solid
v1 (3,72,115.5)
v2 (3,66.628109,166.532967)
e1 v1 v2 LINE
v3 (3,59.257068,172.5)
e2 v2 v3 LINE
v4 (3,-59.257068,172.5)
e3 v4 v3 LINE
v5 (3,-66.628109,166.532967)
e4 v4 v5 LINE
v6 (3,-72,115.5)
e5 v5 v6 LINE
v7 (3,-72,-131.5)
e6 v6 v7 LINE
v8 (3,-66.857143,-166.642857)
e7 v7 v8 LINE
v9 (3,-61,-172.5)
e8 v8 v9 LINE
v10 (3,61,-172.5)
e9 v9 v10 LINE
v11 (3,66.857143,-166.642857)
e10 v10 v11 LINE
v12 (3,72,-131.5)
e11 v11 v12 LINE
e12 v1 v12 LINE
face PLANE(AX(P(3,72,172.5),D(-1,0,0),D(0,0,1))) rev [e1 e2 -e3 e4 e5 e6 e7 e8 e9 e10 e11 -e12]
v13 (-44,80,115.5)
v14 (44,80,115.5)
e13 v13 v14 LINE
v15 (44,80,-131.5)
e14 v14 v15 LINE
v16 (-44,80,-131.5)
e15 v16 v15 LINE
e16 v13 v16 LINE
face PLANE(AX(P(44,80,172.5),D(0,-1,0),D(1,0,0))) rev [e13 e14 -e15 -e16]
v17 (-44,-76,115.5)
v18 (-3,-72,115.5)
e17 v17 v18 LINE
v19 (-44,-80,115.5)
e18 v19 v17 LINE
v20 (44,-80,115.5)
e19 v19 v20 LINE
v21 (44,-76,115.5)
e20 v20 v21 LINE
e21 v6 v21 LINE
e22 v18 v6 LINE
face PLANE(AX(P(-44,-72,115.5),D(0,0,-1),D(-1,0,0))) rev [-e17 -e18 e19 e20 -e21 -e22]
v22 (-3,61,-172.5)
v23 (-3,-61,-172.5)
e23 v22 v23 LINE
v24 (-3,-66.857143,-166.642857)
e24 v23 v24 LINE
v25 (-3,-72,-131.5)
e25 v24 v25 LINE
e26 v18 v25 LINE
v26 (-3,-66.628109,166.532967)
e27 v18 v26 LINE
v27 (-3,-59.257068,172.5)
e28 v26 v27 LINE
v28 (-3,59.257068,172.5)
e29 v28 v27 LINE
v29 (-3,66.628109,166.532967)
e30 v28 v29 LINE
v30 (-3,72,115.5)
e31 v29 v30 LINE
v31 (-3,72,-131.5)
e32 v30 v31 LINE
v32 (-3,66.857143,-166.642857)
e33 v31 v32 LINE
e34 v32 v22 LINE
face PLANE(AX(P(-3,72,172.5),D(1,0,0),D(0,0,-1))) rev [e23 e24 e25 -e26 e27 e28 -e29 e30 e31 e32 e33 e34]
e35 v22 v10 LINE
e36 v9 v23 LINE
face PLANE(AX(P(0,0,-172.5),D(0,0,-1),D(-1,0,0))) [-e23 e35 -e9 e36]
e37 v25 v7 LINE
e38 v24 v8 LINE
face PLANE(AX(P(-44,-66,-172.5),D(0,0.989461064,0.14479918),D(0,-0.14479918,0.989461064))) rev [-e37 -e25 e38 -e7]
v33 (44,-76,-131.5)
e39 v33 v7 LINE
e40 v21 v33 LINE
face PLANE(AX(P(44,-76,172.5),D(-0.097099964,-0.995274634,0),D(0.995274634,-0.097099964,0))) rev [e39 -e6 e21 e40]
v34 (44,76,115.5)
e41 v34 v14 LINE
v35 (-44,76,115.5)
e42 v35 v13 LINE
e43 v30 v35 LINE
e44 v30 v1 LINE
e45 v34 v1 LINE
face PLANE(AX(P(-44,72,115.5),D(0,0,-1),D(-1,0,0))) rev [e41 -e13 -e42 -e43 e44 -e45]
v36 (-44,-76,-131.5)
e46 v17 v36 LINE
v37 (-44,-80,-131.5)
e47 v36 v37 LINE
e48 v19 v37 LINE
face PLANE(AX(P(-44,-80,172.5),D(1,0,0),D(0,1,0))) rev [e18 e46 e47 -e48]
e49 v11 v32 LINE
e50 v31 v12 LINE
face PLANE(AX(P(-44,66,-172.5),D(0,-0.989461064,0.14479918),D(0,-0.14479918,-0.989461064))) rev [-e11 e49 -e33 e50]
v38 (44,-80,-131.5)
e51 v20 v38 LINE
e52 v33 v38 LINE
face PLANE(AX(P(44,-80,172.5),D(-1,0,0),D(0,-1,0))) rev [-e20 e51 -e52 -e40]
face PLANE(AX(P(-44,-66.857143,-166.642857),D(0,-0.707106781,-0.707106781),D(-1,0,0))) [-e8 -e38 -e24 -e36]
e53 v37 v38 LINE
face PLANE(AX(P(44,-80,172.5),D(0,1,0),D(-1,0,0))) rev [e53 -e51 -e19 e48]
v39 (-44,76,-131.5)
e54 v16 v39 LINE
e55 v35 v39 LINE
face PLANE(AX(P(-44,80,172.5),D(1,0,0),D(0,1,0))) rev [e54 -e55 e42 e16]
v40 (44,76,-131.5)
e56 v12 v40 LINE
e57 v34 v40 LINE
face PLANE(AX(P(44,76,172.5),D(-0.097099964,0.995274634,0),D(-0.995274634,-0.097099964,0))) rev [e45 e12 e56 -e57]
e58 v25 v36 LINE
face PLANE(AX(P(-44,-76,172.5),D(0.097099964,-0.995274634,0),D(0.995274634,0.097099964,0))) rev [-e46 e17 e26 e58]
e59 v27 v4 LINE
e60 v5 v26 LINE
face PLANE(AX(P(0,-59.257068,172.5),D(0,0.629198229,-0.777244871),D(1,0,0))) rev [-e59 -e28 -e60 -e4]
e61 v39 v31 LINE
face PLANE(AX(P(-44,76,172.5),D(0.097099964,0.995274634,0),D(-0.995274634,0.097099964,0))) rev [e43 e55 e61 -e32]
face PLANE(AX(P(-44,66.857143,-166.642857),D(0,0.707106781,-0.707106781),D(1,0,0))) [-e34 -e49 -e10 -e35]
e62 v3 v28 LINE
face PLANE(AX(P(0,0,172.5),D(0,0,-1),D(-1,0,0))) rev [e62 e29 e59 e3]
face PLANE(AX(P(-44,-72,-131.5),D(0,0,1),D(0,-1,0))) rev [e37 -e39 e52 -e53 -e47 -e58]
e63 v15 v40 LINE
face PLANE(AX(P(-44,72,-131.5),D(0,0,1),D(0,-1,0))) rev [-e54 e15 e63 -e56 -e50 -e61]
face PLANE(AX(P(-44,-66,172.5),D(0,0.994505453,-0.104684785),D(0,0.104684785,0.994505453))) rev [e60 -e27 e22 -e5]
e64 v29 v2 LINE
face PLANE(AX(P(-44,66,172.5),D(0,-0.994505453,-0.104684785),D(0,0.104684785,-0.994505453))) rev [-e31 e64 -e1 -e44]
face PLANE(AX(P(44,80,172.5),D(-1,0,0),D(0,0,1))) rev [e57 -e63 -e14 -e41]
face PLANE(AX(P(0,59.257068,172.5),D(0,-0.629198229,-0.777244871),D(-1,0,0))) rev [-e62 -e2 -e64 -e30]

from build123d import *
from OCP.BRepFilletAPI import BRepFilletAPI_MakeChamfer

# Parameters (mm, degrees)
EXTRUDE_1_DEPTH          = 172.5
CUT_EXTRUDE_1_DEPTH      = 196.172359723
CUT_EXTRUDE_1_DEPTH_BACK = 196.172359723
CHAMFER_1_SIZE           = 6
CHAMFER_1_SIZE2          = 6.742931709
CHAMFER_2_SIZE           = 5
CHAMFER_2_SIZE2          = 5.919528387
CHAMFER_2_EDGE_2_SIZE    = 5
CHAMFER_2_EDGE_2_SIZE2   = 5.919528387


with BuildPart() as part:
    # 草图1 → 凸台-拉伸1 (new, symmetric)
    with BuildSketch(Plane.XY):
        Polygon((44, 80), (-44, 80), (-44, 76), (-3, 72), (-3, -72), (-44, -76), (-44, -80), (44, -80), (44, -76), (3, -72), (3, 72), (44, 76), align=None)
    extrude(amount=EXTRUDE_1_DEPTH, both=True)

    # 草图3 → 切除-拉伸1 (cut, two sides: drawn at the far end of the back side and taken through both)
    with BuildSketch(Plane(origin=(0, 0, 0), x_dir=(0, 0, -1), z_dir=(1, 0, 0)).offset(-CUT_EXTRUDE_1_DEPTH_BACK)):
        Polygon((-172.5, 66), (-115.5, 72), (-115.5, 80), (-172.5, 80), align=None)
        Polygon((172.5, 80), (172.5, 66), (131.5, 72), (131.5, 80), align=None)
        Polygon((172.5, -66), (131.5, -72), (131.5, -80), (172.5, -80), align=None)
        Polygon((-172.5, -80), (-172.5, -66), (-115.5, -72), (-115.5, -80), align=None)
    extrude(amount=CUT_EXTRUDE_1_DEPTH + CUT_EXTRUDE_1_DEPTH_BACK, mode=Mode.SUBTRACT)

    # 倒角1: one chamfer whose edges measure the first distance from different faces: ONE call of the kernel's chamfer builder (chamfer() names one face for all edges)
    chamfer_1_edges_1 = [part.edges().sort_by_distance(p)[0] for p in [
        (0, 66, 172.5),
    ]]
    chamfer_1_side_1 = [part.faces().sort_by_distance(p)[0] for p in [
        (0, 69, 144),
    ]]
    chamfer_1_edges_2 = [part.edges().sort_by_distance(p)[0] for p in [
        (0, -66, 172.5),
    ]]
    chamfer_1_side_2 = [part.faces().sort_by_distance(p)[0] for p in [
        (0, -69, 144),
    ]]
    chamfer_1 = BRepFilletAPI_MakeChamfer(part.part.solid().wrapped)
    for e in chamfer_1_edges_1:
        chamfer_1.Add(CHAMFER_1_SIZE, CHAMFER_1_SIZE2, e.wrapped, chamfer_1_side_1[0].wrapped)  # the first distance lies on this face
    for e in chamfer_1_edges_2:
        chamfer_1.Add(CHAMFER_1_SIZE, CHAMFER_1_SIZE2, e.wrapped, chamfer_1_side_2[0].wrapped)  # the first distance lies on this face
    add(Compound.cast(chamfer_1.Shape()), mode=Mode.REPLACE)

    # 倒角2
    chamfer_2_edges = [part.edges().sort_by_distance(p)[0] for p in [
        (0, 66, -172.5),
    ]]
    chamfer_2_side = [part.faces().sort_by_distance(p)[0] for p in [
        (0, 0, -172.5),
    ]]
    chamfer(chamfer_2_edges, length=CHAMFER_2_SIZE, length2=CHAMFER_2_SIZE2, reference=chamfer_2_side[0])

    # 倒角2 edge 2
    chamfer_2_edge_2_edges = [part.edges().sort_by_distance(p)[0] for p in [
        (0, -66, -172.5),
    ]]
    chamfer_2_edge_2_side = [part.faces().sort_by_distance(p)[0] for p in [
        (0, 0, -172.5),
    ]]
    chamfer(chamfer_2_edge_2_edges, length=CHAMFER_2_EDGE_2_SIZE, length2=CHAMFER_2_EDGE_2_SIZE2, reference=chamfer_2_edge_2_side[0])


solid = part.part
